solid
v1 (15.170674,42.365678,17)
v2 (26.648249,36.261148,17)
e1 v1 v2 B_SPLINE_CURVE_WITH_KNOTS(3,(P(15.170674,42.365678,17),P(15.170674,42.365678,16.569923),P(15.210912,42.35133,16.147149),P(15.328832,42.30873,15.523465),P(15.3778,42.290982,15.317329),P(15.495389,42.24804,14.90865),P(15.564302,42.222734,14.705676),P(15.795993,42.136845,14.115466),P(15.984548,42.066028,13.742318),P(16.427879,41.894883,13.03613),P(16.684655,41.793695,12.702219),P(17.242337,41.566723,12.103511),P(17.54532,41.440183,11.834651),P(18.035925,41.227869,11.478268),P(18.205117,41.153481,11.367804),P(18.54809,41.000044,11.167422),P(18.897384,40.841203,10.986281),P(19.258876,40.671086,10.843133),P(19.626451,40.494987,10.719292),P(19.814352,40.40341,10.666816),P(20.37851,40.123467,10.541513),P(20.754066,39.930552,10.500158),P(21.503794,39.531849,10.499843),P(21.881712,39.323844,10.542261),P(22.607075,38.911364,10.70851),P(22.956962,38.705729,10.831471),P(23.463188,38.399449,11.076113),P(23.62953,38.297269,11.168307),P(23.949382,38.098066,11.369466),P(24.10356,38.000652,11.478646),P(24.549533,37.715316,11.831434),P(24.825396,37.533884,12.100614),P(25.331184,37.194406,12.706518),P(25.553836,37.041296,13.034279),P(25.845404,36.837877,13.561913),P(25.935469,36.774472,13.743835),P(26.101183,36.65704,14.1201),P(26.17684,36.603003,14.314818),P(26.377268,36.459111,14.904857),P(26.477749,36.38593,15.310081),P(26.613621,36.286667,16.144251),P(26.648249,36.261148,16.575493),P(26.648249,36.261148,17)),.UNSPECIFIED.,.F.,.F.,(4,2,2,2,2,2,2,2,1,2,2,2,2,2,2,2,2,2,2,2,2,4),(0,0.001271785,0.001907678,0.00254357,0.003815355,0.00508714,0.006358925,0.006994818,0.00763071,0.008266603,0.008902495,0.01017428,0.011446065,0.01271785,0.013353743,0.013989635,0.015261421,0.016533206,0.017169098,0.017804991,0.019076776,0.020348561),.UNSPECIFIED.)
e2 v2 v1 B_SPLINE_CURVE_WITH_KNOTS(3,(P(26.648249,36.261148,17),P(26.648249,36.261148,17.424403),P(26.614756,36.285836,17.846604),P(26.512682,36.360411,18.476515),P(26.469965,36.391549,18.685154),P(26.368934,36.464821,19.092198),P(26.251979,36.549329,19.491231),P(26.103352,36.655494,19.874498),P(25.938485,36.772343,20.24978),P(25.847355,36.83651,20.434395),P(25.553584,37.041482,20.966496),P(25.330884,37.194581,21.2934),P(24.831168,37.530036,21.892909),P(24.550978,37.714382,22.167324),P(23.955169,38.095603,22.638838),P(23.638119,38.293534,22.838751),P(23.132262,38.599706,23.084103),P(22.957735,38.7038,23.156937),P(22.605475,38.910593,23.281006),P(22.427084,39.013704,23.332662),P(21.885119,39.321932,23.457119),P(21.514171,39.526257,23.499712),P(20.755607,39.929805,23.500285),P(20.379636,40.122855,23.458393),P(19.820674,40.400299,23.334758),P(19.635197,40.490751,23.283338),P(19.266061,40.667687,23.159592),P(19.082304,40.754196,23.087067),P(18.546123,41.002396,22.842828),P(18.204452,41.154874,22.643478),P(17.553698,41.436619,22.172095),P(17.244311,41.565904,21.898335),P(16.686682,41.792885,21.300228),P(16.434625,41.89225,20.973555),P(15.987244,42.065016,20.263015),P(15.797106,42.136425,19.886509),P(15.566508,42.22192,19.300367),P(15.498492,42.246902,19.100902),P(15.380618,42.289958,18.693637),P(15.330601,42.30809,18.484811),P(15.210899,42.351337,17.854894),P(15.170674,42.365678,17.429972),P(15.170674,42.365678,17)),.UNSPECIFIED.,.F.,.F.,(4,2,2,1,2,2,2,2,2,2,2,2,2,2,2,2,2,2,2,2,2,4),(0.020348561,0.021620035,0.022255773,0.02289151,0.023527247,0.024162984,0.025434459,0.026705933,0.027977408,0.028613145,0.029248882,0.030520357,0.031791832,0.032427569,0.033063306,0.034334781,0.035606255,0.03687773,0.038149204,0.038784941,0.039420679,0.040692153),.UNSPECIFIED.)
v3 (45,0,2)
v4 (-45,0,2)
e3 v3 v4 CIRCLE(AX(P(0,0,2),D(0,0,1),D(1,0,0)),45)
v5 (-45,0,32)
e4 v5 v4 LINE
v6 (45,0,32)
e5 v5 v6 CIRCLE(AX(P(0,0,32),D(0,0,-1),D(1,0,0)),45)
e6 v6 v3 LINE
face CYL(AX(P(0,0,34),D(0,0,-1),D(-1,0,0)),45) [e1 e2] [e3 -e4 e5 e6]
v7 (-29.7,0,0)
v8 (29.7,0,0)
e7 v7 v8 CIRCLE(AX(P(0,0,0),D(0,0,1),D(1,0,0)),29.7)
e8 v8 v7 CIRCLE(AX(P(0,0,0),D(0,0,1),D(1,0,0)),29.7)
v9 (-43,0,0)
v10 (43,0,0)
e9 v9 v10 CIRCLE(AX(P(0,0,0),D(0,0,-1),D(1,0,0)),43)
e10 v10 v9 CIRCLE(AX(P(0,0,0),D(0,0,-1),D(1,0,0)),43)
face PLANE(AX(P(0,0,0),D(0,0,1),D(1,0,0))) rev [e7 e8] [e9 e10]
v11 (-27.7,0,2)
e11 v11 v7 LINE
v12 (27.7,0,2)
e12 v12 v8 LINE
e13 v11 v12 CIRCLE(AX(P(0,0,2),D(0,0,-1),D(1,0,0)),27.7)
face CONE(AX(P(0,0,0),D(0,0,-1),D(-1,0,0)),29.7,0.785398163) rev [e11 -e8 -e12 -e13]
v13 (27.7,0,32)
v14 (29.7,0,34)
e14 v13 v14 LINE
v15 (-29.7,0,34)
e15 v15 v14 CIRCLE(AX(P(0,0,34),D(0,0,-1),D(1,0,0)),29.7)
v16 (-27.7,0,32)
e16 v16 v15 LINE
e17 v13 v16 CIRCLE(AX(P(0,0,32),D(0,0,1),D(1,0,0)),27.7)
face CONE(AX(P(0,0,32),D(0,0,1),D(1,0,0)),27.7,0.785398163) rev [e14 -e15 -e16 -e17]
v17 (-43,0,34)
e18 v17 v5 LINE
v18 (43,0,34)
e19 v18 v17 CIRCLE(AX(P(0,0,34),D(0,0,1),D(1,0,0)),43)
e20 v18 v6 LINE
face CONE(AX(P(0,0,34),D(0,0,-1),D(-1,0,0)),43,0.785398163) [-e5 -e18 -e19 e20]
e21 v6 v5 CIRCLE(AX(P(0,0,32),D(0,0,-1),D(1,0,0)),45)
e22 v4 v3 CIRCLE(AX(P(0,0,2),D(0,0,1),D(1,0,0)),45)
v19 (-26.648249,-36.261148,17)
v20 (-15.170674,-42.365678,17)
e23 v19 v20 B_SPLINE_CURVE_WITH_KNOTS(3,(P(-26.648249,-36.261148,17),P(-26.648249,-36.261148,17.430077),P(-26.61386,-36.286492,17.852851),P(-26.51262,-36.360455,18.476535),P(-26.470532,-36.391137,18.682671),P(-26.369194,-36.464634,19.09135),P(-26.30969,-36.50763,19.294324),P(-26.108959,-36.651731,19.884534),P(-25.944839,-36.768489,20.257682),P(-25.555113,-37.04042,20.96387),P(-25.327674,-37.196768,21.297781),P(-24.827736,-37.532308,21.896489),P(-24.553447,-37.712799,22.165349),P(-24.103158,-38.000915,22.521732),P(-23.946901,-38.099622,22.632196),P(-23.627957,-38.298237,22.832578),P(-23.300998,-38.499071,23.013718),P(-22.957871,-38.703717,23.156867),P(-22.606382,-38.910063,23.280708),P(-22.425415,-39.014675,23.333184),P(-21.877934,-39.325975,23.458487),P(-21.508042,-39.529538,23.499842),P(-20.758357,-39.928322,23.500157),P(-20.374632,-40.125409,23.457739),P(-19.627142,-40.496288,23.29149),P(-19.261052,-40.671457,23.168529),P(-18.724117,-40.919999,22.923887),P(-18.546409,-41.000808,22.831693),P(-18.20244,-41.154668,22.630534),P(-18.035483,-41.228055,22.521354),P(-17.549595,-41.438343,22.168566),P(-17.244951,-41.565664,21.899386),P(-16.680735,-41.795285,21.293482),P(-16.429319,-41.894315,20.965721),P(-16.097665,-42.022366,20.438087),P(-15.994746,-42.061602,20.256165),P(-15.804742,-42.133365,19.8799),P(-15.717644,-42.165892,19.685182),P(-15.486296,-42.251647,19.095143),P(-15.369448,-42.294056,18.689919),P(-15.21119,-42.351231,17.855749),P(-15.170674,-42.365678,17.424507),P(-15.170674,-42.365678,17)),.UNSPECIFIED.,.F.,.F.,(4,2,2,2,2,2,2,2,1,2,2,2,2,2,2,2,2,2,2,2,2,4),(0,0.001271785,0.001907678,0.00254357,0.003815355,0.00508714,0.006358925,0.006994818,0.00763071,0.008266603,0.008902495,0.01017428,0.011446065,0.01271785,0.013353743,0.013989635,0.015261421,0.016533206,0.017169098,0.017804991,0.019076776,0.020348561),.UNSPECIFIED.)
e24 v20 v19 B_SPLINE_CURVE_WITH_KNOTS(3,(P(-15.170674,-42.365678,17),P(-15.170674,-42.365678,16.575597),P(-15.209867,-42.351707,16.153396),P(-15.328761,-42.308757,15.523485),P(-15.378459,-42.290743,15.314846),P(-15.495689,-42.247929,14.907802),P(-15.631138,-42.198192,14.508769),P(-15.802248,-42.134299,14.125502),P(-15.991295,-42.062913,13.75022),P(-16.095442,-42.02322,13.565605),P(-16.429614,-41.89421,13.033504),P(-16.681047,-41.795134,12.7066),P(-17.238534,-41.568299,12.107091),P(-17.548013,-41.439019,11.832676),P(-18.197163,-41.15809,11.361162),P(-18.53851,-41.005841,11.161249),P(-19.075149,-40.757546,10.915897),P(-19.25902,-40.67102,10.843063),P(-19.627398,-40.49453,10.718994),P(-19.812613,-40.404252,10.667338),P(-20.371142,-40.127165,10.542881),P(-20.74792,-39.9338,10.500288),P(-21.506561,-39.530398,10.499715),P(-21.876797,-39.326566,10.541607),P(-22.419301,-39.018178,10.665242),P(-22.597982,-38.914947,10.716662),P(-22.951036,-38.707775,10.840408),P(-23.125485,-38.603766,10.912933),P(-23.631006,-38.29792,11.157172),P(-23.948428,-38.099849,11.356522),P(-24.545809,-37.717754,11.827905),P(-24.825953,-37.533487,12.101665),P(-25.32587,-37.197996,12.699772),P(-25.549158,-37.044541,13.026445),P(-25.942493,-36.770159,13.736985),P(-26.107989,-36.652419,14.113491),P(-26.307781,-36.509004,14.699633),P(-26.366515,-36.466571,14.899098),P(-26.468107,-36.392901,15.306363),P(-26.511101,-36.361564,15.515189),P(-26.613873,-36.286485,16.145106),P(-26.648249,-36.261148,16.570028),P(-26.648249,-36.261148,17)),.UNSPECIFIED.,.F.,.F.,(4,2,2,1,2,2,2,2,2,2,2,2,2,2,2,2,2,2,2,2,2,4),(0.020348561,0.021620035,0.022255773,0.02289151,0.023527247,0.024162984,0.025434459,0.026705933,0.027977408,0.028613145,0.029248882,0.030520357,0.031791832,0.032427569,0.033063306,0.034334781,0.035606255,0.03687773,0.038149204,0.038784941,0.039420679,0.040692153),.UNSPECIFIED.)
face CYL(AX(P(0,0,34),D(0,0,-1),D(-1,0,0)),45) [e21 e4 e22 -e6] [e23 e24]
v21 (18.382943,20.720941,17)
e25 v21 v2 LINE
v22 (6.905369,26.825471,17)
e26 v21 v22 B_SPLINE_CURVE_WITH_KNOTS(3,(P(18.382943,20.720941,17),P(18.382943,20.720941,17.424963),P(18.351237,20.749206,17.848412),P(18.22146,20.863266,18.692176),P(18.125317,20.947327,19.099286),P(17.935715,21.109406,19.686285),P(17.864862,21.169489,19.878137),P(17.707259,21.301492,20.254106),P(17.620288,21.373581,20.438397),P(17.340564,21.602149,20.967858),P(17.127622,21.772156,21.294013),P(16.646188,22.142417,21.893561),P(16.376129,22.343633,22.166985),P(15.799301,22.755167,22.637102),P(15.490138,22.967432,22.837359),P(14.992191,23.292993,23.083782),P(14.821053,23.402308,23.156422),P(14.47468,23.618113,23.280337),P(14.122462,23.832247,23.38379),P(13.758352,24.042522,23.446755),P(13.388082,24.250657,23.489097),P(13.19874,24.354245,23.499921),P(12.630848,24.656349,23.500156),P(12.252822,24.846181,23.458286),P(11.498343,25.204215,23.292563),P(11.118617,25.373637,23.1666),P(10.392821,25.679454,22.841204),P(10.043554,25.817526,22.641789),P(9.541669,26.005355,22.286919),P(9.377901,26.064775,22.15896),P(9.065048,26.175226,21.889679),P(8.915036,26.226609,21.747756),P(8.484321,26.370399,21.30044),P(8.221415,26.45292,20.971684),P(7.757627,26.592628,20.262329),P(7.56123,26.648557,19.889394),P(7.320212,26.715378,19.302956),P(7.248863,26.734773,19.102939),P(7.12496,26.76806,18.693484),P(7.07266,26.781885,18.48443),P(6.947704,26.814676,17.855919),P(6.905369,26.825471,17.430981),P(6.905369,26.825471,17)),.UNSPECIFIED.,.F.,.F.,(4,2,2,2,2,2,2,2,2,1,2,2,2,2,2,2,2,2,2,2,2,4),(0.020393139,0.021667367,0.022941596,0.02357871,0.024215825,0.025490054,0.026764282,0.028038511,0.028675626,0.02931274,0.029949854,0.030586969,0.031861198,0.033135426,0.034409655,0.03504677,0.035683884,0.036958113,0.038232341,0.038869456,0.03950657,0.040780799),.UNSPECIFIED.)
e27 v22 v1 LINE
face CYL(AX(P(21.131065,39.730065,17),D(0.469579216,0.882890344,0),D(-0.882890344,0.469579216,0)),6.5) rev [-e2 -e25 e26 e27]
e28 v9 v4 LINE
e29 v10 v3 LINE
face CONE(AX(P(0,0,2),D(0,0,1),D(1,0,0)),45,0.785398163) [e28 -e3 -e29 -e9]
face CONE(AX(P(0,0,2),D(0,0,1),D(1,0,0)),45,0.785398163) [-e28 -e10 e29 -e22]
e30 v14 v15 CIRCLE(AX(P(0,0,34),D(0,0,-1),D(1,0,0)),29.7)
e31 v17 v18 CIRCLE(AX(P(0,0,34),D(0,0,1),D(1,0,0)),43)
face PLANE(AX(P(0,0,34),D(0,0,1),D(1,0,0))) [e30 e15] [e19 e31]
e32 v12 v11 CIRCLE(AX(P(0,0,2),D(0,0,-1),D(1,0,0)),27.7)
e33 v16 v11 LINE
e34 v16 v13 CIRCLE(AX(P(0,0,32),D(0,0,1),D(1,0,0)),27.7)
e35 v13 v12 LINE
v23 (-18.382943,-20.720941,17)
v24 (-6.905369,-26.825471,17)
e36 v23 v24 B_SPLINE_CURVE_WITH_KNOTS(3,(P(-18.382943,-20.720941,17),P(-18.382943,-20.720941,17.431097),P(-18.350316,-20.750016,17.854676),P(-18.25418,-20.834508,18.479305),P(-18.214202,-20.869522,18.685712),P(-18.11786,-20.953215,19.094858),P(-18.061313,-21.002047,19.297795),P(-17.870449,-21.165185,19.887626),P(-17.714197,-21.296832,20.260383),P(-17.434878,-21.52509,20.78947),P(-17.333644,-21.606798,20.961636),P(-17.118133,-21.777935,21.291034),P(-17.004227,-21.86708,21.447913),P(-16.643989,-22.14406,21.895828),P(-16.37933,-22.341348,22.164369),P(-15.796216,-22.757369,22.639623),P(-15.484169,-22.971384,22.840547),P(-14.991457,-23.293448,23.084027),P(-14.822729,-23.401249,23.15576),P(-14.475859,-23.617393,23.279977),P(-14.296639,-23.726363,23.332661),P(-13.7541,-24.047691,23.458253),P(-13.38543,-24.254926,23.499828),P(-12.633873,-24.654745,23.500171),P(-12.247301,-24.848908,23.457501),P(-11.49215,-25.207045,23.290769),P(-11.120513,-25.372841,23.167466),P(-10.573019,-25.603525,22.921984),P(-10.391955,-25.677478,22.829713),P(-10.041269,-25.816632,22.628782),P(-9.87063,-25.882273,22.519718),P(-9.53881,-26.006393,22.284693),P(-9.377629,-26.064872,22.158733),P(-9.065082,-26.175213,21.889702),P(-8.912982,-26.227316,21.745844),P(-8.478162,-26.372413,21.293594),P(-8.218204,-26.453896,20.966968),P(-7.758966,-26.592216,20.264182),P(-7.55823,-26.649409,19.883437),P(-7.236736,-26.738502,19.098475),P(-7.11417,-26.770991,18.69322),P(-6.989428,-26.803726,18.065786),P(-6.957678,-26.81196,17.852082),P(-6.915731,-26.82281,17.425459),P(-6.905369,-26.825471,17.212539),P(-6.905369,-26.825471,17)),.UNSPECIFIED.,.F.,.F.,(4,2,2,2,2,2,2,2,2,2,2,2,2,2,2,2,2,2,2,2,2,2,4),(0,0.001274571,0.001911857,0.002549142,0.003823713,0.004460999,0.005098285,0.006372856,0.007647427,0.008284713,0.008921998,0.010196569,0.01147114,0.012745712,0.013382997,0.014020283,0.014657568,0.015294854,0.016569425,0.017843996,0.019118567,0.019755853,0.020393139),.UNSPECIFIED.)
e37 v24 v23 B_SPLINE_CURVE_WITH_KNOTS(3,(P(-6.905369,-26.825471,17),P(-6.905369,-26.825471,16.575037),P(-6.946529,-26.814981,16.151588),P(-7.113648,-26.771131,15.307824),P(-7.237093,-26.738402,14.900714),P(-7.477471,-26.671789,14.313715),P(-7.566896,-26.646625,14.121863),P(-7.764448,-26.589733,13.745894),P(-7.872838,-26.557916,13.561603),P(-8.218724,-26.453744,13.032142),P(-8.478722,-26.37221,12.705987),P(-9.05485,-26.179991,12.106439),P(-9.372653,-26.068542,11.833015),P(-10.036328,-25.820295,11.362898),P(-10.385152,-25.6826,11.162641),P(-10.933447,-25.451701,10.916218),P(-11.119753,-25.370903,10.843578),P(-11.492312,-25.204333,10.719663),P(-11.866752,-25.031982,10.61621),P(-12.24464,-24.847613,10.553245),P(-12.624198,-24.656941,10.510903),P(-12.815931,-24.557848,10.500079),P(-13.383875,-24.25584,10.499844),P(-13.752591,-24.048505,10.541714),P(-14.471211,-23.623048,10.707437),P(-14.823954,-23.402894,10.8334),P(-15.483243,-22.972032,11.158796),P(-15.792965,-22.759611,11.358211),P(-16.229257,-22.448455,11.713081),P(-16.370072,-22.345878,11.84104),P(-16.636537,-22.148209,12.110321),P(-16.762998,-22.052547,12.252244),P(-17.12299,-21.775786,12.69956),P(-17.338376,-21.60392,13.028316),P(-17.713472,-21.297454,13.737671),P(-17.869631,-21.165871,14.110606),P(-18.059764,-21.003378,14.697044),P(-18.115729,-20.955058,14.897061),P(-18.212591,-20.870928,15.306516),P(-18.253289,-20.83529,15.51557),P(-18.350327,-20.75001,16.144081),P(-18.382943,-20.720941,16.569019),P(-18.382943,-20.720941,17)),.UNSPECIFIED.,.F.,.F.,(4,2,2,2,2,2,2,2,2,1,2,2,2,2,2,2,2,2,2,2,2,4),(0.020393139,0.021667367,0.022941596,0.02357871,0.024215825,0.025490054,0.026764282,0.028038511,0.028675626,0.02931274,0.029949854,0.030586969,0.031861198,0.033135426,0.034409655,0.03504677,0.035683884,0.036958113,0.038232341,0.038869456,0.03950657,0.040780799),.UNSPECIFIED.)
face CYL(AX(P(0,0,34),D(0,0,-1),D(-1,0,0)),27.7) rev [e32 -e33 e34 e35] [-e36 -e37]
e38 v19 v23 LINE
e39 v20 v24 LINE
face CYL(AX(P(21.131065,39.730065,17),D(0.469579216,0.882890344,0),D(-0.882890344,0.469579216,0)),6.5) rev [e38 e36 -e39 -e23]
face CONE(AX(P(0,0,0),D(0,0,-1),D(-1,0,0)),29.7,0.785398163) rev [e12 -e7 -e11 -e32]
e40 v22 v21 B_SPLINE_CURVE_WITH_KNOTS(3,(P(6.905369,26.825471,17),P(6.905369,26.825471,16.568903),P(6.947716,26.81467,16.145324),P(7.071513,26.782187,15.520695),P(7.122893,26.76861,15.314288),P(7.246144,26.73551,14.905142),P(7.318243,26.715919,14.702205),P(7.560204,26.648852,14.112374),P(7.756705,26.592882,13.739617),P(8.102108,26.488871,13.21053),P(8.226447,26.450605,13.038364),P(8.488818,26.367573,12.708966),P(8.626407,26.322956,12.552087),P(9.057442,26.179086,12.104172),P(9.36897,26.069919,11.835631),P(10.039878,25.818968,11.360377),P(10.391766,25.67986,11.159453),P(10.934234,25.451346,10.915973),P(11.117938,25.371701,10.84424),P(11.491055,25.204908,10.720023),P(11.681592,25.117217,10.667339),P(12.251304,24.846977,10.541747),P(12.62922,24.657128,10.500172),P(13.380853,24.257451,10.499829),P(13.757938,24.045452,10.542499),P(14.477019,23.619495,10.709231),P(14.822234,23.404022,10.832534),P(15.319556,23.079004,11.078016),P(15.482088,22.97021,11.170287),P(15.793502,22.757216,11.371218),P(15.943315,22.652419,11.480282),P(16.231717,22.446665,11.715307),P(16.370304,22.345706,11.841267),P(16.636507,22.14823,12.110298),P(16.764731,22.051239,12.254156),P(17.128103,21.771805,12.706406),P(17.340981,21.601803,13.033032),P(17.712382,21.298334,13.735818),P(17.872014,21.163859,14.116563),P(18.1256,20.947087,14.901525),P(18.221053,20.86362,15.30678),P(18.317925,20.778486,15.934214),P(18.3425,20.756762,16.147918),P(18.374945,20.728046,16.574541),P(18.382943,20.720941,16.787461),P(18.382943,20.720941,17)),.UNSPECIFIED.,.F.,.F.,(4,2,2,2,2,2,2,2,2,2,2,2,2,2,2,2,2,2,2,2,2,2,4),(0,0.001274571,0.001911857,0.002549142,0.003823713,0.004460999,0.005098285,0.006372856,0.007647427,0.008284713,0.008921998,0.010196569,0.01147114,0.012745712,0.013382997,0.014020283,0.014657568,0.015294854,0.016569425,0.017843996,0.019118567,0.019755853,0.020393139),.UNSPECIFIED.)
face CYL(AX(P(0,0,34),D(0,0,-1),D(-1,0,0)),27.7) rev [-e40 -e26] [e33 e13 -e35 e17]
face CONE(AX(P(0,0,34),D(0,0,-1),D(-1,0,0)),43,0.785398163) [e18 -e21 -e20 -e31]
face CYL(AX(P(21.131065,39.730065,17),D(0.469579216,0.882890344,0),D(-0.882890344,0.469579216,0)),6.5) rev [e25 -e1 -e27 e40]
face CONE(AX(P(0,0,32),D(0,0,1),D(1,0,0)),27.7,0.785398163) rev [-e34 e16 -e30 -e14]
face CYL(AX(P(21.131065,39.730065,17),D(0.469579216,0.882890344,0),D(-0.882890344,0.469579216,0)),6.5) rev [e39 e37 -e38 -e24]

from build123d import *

# Parameters (mm, degrees)
SKETCH1_R                  = 45
SKETCH1_R_2                = 27.7
BOSS_EXTRUDE1_DEPTH        = 34
F_13_0_13_DIAMETER_HOLE1_D = 13
CHAMFER1_SIZE              = 2


with BuildPart() as part:
    # Sketch1 → Boss-Extrude1 (new body)
    with BuildSketch(Plane.XY):
        Circle(SKETCH1_R)
        Circle(SKETCH1_R_2, mode=Mode.SUBTRACT)
    extrude(amount=BOSS_EXTRUDE1_DEPTH)

    # Ø13.0 (13) Diameter Hole1 (through all)
    with Locations(Plane(origin=(21.131064714, 39.730065493, 17), x_dir=(0.882890344282, -0.469579215865, 0), z_dir=(0.469579215865, 0.882890344282, 0))):
        with Locations((0, 0)):
            Hole(F_13_0_13_DIAMETER_HOLE1_D / 2)

    # Chamfer1
    chamfer1_edges = [part.edges().sort_by_distance(p)[0] for p in [
        (-45, 0, 0),
        (-45, 0, 34),
        (-27.7, 0, 0),
        (-27.7, 0, 34),
    ]]
    chamfer(chamfer1_edges, length=CHAMFER1_SIZE)


solid = part.part
